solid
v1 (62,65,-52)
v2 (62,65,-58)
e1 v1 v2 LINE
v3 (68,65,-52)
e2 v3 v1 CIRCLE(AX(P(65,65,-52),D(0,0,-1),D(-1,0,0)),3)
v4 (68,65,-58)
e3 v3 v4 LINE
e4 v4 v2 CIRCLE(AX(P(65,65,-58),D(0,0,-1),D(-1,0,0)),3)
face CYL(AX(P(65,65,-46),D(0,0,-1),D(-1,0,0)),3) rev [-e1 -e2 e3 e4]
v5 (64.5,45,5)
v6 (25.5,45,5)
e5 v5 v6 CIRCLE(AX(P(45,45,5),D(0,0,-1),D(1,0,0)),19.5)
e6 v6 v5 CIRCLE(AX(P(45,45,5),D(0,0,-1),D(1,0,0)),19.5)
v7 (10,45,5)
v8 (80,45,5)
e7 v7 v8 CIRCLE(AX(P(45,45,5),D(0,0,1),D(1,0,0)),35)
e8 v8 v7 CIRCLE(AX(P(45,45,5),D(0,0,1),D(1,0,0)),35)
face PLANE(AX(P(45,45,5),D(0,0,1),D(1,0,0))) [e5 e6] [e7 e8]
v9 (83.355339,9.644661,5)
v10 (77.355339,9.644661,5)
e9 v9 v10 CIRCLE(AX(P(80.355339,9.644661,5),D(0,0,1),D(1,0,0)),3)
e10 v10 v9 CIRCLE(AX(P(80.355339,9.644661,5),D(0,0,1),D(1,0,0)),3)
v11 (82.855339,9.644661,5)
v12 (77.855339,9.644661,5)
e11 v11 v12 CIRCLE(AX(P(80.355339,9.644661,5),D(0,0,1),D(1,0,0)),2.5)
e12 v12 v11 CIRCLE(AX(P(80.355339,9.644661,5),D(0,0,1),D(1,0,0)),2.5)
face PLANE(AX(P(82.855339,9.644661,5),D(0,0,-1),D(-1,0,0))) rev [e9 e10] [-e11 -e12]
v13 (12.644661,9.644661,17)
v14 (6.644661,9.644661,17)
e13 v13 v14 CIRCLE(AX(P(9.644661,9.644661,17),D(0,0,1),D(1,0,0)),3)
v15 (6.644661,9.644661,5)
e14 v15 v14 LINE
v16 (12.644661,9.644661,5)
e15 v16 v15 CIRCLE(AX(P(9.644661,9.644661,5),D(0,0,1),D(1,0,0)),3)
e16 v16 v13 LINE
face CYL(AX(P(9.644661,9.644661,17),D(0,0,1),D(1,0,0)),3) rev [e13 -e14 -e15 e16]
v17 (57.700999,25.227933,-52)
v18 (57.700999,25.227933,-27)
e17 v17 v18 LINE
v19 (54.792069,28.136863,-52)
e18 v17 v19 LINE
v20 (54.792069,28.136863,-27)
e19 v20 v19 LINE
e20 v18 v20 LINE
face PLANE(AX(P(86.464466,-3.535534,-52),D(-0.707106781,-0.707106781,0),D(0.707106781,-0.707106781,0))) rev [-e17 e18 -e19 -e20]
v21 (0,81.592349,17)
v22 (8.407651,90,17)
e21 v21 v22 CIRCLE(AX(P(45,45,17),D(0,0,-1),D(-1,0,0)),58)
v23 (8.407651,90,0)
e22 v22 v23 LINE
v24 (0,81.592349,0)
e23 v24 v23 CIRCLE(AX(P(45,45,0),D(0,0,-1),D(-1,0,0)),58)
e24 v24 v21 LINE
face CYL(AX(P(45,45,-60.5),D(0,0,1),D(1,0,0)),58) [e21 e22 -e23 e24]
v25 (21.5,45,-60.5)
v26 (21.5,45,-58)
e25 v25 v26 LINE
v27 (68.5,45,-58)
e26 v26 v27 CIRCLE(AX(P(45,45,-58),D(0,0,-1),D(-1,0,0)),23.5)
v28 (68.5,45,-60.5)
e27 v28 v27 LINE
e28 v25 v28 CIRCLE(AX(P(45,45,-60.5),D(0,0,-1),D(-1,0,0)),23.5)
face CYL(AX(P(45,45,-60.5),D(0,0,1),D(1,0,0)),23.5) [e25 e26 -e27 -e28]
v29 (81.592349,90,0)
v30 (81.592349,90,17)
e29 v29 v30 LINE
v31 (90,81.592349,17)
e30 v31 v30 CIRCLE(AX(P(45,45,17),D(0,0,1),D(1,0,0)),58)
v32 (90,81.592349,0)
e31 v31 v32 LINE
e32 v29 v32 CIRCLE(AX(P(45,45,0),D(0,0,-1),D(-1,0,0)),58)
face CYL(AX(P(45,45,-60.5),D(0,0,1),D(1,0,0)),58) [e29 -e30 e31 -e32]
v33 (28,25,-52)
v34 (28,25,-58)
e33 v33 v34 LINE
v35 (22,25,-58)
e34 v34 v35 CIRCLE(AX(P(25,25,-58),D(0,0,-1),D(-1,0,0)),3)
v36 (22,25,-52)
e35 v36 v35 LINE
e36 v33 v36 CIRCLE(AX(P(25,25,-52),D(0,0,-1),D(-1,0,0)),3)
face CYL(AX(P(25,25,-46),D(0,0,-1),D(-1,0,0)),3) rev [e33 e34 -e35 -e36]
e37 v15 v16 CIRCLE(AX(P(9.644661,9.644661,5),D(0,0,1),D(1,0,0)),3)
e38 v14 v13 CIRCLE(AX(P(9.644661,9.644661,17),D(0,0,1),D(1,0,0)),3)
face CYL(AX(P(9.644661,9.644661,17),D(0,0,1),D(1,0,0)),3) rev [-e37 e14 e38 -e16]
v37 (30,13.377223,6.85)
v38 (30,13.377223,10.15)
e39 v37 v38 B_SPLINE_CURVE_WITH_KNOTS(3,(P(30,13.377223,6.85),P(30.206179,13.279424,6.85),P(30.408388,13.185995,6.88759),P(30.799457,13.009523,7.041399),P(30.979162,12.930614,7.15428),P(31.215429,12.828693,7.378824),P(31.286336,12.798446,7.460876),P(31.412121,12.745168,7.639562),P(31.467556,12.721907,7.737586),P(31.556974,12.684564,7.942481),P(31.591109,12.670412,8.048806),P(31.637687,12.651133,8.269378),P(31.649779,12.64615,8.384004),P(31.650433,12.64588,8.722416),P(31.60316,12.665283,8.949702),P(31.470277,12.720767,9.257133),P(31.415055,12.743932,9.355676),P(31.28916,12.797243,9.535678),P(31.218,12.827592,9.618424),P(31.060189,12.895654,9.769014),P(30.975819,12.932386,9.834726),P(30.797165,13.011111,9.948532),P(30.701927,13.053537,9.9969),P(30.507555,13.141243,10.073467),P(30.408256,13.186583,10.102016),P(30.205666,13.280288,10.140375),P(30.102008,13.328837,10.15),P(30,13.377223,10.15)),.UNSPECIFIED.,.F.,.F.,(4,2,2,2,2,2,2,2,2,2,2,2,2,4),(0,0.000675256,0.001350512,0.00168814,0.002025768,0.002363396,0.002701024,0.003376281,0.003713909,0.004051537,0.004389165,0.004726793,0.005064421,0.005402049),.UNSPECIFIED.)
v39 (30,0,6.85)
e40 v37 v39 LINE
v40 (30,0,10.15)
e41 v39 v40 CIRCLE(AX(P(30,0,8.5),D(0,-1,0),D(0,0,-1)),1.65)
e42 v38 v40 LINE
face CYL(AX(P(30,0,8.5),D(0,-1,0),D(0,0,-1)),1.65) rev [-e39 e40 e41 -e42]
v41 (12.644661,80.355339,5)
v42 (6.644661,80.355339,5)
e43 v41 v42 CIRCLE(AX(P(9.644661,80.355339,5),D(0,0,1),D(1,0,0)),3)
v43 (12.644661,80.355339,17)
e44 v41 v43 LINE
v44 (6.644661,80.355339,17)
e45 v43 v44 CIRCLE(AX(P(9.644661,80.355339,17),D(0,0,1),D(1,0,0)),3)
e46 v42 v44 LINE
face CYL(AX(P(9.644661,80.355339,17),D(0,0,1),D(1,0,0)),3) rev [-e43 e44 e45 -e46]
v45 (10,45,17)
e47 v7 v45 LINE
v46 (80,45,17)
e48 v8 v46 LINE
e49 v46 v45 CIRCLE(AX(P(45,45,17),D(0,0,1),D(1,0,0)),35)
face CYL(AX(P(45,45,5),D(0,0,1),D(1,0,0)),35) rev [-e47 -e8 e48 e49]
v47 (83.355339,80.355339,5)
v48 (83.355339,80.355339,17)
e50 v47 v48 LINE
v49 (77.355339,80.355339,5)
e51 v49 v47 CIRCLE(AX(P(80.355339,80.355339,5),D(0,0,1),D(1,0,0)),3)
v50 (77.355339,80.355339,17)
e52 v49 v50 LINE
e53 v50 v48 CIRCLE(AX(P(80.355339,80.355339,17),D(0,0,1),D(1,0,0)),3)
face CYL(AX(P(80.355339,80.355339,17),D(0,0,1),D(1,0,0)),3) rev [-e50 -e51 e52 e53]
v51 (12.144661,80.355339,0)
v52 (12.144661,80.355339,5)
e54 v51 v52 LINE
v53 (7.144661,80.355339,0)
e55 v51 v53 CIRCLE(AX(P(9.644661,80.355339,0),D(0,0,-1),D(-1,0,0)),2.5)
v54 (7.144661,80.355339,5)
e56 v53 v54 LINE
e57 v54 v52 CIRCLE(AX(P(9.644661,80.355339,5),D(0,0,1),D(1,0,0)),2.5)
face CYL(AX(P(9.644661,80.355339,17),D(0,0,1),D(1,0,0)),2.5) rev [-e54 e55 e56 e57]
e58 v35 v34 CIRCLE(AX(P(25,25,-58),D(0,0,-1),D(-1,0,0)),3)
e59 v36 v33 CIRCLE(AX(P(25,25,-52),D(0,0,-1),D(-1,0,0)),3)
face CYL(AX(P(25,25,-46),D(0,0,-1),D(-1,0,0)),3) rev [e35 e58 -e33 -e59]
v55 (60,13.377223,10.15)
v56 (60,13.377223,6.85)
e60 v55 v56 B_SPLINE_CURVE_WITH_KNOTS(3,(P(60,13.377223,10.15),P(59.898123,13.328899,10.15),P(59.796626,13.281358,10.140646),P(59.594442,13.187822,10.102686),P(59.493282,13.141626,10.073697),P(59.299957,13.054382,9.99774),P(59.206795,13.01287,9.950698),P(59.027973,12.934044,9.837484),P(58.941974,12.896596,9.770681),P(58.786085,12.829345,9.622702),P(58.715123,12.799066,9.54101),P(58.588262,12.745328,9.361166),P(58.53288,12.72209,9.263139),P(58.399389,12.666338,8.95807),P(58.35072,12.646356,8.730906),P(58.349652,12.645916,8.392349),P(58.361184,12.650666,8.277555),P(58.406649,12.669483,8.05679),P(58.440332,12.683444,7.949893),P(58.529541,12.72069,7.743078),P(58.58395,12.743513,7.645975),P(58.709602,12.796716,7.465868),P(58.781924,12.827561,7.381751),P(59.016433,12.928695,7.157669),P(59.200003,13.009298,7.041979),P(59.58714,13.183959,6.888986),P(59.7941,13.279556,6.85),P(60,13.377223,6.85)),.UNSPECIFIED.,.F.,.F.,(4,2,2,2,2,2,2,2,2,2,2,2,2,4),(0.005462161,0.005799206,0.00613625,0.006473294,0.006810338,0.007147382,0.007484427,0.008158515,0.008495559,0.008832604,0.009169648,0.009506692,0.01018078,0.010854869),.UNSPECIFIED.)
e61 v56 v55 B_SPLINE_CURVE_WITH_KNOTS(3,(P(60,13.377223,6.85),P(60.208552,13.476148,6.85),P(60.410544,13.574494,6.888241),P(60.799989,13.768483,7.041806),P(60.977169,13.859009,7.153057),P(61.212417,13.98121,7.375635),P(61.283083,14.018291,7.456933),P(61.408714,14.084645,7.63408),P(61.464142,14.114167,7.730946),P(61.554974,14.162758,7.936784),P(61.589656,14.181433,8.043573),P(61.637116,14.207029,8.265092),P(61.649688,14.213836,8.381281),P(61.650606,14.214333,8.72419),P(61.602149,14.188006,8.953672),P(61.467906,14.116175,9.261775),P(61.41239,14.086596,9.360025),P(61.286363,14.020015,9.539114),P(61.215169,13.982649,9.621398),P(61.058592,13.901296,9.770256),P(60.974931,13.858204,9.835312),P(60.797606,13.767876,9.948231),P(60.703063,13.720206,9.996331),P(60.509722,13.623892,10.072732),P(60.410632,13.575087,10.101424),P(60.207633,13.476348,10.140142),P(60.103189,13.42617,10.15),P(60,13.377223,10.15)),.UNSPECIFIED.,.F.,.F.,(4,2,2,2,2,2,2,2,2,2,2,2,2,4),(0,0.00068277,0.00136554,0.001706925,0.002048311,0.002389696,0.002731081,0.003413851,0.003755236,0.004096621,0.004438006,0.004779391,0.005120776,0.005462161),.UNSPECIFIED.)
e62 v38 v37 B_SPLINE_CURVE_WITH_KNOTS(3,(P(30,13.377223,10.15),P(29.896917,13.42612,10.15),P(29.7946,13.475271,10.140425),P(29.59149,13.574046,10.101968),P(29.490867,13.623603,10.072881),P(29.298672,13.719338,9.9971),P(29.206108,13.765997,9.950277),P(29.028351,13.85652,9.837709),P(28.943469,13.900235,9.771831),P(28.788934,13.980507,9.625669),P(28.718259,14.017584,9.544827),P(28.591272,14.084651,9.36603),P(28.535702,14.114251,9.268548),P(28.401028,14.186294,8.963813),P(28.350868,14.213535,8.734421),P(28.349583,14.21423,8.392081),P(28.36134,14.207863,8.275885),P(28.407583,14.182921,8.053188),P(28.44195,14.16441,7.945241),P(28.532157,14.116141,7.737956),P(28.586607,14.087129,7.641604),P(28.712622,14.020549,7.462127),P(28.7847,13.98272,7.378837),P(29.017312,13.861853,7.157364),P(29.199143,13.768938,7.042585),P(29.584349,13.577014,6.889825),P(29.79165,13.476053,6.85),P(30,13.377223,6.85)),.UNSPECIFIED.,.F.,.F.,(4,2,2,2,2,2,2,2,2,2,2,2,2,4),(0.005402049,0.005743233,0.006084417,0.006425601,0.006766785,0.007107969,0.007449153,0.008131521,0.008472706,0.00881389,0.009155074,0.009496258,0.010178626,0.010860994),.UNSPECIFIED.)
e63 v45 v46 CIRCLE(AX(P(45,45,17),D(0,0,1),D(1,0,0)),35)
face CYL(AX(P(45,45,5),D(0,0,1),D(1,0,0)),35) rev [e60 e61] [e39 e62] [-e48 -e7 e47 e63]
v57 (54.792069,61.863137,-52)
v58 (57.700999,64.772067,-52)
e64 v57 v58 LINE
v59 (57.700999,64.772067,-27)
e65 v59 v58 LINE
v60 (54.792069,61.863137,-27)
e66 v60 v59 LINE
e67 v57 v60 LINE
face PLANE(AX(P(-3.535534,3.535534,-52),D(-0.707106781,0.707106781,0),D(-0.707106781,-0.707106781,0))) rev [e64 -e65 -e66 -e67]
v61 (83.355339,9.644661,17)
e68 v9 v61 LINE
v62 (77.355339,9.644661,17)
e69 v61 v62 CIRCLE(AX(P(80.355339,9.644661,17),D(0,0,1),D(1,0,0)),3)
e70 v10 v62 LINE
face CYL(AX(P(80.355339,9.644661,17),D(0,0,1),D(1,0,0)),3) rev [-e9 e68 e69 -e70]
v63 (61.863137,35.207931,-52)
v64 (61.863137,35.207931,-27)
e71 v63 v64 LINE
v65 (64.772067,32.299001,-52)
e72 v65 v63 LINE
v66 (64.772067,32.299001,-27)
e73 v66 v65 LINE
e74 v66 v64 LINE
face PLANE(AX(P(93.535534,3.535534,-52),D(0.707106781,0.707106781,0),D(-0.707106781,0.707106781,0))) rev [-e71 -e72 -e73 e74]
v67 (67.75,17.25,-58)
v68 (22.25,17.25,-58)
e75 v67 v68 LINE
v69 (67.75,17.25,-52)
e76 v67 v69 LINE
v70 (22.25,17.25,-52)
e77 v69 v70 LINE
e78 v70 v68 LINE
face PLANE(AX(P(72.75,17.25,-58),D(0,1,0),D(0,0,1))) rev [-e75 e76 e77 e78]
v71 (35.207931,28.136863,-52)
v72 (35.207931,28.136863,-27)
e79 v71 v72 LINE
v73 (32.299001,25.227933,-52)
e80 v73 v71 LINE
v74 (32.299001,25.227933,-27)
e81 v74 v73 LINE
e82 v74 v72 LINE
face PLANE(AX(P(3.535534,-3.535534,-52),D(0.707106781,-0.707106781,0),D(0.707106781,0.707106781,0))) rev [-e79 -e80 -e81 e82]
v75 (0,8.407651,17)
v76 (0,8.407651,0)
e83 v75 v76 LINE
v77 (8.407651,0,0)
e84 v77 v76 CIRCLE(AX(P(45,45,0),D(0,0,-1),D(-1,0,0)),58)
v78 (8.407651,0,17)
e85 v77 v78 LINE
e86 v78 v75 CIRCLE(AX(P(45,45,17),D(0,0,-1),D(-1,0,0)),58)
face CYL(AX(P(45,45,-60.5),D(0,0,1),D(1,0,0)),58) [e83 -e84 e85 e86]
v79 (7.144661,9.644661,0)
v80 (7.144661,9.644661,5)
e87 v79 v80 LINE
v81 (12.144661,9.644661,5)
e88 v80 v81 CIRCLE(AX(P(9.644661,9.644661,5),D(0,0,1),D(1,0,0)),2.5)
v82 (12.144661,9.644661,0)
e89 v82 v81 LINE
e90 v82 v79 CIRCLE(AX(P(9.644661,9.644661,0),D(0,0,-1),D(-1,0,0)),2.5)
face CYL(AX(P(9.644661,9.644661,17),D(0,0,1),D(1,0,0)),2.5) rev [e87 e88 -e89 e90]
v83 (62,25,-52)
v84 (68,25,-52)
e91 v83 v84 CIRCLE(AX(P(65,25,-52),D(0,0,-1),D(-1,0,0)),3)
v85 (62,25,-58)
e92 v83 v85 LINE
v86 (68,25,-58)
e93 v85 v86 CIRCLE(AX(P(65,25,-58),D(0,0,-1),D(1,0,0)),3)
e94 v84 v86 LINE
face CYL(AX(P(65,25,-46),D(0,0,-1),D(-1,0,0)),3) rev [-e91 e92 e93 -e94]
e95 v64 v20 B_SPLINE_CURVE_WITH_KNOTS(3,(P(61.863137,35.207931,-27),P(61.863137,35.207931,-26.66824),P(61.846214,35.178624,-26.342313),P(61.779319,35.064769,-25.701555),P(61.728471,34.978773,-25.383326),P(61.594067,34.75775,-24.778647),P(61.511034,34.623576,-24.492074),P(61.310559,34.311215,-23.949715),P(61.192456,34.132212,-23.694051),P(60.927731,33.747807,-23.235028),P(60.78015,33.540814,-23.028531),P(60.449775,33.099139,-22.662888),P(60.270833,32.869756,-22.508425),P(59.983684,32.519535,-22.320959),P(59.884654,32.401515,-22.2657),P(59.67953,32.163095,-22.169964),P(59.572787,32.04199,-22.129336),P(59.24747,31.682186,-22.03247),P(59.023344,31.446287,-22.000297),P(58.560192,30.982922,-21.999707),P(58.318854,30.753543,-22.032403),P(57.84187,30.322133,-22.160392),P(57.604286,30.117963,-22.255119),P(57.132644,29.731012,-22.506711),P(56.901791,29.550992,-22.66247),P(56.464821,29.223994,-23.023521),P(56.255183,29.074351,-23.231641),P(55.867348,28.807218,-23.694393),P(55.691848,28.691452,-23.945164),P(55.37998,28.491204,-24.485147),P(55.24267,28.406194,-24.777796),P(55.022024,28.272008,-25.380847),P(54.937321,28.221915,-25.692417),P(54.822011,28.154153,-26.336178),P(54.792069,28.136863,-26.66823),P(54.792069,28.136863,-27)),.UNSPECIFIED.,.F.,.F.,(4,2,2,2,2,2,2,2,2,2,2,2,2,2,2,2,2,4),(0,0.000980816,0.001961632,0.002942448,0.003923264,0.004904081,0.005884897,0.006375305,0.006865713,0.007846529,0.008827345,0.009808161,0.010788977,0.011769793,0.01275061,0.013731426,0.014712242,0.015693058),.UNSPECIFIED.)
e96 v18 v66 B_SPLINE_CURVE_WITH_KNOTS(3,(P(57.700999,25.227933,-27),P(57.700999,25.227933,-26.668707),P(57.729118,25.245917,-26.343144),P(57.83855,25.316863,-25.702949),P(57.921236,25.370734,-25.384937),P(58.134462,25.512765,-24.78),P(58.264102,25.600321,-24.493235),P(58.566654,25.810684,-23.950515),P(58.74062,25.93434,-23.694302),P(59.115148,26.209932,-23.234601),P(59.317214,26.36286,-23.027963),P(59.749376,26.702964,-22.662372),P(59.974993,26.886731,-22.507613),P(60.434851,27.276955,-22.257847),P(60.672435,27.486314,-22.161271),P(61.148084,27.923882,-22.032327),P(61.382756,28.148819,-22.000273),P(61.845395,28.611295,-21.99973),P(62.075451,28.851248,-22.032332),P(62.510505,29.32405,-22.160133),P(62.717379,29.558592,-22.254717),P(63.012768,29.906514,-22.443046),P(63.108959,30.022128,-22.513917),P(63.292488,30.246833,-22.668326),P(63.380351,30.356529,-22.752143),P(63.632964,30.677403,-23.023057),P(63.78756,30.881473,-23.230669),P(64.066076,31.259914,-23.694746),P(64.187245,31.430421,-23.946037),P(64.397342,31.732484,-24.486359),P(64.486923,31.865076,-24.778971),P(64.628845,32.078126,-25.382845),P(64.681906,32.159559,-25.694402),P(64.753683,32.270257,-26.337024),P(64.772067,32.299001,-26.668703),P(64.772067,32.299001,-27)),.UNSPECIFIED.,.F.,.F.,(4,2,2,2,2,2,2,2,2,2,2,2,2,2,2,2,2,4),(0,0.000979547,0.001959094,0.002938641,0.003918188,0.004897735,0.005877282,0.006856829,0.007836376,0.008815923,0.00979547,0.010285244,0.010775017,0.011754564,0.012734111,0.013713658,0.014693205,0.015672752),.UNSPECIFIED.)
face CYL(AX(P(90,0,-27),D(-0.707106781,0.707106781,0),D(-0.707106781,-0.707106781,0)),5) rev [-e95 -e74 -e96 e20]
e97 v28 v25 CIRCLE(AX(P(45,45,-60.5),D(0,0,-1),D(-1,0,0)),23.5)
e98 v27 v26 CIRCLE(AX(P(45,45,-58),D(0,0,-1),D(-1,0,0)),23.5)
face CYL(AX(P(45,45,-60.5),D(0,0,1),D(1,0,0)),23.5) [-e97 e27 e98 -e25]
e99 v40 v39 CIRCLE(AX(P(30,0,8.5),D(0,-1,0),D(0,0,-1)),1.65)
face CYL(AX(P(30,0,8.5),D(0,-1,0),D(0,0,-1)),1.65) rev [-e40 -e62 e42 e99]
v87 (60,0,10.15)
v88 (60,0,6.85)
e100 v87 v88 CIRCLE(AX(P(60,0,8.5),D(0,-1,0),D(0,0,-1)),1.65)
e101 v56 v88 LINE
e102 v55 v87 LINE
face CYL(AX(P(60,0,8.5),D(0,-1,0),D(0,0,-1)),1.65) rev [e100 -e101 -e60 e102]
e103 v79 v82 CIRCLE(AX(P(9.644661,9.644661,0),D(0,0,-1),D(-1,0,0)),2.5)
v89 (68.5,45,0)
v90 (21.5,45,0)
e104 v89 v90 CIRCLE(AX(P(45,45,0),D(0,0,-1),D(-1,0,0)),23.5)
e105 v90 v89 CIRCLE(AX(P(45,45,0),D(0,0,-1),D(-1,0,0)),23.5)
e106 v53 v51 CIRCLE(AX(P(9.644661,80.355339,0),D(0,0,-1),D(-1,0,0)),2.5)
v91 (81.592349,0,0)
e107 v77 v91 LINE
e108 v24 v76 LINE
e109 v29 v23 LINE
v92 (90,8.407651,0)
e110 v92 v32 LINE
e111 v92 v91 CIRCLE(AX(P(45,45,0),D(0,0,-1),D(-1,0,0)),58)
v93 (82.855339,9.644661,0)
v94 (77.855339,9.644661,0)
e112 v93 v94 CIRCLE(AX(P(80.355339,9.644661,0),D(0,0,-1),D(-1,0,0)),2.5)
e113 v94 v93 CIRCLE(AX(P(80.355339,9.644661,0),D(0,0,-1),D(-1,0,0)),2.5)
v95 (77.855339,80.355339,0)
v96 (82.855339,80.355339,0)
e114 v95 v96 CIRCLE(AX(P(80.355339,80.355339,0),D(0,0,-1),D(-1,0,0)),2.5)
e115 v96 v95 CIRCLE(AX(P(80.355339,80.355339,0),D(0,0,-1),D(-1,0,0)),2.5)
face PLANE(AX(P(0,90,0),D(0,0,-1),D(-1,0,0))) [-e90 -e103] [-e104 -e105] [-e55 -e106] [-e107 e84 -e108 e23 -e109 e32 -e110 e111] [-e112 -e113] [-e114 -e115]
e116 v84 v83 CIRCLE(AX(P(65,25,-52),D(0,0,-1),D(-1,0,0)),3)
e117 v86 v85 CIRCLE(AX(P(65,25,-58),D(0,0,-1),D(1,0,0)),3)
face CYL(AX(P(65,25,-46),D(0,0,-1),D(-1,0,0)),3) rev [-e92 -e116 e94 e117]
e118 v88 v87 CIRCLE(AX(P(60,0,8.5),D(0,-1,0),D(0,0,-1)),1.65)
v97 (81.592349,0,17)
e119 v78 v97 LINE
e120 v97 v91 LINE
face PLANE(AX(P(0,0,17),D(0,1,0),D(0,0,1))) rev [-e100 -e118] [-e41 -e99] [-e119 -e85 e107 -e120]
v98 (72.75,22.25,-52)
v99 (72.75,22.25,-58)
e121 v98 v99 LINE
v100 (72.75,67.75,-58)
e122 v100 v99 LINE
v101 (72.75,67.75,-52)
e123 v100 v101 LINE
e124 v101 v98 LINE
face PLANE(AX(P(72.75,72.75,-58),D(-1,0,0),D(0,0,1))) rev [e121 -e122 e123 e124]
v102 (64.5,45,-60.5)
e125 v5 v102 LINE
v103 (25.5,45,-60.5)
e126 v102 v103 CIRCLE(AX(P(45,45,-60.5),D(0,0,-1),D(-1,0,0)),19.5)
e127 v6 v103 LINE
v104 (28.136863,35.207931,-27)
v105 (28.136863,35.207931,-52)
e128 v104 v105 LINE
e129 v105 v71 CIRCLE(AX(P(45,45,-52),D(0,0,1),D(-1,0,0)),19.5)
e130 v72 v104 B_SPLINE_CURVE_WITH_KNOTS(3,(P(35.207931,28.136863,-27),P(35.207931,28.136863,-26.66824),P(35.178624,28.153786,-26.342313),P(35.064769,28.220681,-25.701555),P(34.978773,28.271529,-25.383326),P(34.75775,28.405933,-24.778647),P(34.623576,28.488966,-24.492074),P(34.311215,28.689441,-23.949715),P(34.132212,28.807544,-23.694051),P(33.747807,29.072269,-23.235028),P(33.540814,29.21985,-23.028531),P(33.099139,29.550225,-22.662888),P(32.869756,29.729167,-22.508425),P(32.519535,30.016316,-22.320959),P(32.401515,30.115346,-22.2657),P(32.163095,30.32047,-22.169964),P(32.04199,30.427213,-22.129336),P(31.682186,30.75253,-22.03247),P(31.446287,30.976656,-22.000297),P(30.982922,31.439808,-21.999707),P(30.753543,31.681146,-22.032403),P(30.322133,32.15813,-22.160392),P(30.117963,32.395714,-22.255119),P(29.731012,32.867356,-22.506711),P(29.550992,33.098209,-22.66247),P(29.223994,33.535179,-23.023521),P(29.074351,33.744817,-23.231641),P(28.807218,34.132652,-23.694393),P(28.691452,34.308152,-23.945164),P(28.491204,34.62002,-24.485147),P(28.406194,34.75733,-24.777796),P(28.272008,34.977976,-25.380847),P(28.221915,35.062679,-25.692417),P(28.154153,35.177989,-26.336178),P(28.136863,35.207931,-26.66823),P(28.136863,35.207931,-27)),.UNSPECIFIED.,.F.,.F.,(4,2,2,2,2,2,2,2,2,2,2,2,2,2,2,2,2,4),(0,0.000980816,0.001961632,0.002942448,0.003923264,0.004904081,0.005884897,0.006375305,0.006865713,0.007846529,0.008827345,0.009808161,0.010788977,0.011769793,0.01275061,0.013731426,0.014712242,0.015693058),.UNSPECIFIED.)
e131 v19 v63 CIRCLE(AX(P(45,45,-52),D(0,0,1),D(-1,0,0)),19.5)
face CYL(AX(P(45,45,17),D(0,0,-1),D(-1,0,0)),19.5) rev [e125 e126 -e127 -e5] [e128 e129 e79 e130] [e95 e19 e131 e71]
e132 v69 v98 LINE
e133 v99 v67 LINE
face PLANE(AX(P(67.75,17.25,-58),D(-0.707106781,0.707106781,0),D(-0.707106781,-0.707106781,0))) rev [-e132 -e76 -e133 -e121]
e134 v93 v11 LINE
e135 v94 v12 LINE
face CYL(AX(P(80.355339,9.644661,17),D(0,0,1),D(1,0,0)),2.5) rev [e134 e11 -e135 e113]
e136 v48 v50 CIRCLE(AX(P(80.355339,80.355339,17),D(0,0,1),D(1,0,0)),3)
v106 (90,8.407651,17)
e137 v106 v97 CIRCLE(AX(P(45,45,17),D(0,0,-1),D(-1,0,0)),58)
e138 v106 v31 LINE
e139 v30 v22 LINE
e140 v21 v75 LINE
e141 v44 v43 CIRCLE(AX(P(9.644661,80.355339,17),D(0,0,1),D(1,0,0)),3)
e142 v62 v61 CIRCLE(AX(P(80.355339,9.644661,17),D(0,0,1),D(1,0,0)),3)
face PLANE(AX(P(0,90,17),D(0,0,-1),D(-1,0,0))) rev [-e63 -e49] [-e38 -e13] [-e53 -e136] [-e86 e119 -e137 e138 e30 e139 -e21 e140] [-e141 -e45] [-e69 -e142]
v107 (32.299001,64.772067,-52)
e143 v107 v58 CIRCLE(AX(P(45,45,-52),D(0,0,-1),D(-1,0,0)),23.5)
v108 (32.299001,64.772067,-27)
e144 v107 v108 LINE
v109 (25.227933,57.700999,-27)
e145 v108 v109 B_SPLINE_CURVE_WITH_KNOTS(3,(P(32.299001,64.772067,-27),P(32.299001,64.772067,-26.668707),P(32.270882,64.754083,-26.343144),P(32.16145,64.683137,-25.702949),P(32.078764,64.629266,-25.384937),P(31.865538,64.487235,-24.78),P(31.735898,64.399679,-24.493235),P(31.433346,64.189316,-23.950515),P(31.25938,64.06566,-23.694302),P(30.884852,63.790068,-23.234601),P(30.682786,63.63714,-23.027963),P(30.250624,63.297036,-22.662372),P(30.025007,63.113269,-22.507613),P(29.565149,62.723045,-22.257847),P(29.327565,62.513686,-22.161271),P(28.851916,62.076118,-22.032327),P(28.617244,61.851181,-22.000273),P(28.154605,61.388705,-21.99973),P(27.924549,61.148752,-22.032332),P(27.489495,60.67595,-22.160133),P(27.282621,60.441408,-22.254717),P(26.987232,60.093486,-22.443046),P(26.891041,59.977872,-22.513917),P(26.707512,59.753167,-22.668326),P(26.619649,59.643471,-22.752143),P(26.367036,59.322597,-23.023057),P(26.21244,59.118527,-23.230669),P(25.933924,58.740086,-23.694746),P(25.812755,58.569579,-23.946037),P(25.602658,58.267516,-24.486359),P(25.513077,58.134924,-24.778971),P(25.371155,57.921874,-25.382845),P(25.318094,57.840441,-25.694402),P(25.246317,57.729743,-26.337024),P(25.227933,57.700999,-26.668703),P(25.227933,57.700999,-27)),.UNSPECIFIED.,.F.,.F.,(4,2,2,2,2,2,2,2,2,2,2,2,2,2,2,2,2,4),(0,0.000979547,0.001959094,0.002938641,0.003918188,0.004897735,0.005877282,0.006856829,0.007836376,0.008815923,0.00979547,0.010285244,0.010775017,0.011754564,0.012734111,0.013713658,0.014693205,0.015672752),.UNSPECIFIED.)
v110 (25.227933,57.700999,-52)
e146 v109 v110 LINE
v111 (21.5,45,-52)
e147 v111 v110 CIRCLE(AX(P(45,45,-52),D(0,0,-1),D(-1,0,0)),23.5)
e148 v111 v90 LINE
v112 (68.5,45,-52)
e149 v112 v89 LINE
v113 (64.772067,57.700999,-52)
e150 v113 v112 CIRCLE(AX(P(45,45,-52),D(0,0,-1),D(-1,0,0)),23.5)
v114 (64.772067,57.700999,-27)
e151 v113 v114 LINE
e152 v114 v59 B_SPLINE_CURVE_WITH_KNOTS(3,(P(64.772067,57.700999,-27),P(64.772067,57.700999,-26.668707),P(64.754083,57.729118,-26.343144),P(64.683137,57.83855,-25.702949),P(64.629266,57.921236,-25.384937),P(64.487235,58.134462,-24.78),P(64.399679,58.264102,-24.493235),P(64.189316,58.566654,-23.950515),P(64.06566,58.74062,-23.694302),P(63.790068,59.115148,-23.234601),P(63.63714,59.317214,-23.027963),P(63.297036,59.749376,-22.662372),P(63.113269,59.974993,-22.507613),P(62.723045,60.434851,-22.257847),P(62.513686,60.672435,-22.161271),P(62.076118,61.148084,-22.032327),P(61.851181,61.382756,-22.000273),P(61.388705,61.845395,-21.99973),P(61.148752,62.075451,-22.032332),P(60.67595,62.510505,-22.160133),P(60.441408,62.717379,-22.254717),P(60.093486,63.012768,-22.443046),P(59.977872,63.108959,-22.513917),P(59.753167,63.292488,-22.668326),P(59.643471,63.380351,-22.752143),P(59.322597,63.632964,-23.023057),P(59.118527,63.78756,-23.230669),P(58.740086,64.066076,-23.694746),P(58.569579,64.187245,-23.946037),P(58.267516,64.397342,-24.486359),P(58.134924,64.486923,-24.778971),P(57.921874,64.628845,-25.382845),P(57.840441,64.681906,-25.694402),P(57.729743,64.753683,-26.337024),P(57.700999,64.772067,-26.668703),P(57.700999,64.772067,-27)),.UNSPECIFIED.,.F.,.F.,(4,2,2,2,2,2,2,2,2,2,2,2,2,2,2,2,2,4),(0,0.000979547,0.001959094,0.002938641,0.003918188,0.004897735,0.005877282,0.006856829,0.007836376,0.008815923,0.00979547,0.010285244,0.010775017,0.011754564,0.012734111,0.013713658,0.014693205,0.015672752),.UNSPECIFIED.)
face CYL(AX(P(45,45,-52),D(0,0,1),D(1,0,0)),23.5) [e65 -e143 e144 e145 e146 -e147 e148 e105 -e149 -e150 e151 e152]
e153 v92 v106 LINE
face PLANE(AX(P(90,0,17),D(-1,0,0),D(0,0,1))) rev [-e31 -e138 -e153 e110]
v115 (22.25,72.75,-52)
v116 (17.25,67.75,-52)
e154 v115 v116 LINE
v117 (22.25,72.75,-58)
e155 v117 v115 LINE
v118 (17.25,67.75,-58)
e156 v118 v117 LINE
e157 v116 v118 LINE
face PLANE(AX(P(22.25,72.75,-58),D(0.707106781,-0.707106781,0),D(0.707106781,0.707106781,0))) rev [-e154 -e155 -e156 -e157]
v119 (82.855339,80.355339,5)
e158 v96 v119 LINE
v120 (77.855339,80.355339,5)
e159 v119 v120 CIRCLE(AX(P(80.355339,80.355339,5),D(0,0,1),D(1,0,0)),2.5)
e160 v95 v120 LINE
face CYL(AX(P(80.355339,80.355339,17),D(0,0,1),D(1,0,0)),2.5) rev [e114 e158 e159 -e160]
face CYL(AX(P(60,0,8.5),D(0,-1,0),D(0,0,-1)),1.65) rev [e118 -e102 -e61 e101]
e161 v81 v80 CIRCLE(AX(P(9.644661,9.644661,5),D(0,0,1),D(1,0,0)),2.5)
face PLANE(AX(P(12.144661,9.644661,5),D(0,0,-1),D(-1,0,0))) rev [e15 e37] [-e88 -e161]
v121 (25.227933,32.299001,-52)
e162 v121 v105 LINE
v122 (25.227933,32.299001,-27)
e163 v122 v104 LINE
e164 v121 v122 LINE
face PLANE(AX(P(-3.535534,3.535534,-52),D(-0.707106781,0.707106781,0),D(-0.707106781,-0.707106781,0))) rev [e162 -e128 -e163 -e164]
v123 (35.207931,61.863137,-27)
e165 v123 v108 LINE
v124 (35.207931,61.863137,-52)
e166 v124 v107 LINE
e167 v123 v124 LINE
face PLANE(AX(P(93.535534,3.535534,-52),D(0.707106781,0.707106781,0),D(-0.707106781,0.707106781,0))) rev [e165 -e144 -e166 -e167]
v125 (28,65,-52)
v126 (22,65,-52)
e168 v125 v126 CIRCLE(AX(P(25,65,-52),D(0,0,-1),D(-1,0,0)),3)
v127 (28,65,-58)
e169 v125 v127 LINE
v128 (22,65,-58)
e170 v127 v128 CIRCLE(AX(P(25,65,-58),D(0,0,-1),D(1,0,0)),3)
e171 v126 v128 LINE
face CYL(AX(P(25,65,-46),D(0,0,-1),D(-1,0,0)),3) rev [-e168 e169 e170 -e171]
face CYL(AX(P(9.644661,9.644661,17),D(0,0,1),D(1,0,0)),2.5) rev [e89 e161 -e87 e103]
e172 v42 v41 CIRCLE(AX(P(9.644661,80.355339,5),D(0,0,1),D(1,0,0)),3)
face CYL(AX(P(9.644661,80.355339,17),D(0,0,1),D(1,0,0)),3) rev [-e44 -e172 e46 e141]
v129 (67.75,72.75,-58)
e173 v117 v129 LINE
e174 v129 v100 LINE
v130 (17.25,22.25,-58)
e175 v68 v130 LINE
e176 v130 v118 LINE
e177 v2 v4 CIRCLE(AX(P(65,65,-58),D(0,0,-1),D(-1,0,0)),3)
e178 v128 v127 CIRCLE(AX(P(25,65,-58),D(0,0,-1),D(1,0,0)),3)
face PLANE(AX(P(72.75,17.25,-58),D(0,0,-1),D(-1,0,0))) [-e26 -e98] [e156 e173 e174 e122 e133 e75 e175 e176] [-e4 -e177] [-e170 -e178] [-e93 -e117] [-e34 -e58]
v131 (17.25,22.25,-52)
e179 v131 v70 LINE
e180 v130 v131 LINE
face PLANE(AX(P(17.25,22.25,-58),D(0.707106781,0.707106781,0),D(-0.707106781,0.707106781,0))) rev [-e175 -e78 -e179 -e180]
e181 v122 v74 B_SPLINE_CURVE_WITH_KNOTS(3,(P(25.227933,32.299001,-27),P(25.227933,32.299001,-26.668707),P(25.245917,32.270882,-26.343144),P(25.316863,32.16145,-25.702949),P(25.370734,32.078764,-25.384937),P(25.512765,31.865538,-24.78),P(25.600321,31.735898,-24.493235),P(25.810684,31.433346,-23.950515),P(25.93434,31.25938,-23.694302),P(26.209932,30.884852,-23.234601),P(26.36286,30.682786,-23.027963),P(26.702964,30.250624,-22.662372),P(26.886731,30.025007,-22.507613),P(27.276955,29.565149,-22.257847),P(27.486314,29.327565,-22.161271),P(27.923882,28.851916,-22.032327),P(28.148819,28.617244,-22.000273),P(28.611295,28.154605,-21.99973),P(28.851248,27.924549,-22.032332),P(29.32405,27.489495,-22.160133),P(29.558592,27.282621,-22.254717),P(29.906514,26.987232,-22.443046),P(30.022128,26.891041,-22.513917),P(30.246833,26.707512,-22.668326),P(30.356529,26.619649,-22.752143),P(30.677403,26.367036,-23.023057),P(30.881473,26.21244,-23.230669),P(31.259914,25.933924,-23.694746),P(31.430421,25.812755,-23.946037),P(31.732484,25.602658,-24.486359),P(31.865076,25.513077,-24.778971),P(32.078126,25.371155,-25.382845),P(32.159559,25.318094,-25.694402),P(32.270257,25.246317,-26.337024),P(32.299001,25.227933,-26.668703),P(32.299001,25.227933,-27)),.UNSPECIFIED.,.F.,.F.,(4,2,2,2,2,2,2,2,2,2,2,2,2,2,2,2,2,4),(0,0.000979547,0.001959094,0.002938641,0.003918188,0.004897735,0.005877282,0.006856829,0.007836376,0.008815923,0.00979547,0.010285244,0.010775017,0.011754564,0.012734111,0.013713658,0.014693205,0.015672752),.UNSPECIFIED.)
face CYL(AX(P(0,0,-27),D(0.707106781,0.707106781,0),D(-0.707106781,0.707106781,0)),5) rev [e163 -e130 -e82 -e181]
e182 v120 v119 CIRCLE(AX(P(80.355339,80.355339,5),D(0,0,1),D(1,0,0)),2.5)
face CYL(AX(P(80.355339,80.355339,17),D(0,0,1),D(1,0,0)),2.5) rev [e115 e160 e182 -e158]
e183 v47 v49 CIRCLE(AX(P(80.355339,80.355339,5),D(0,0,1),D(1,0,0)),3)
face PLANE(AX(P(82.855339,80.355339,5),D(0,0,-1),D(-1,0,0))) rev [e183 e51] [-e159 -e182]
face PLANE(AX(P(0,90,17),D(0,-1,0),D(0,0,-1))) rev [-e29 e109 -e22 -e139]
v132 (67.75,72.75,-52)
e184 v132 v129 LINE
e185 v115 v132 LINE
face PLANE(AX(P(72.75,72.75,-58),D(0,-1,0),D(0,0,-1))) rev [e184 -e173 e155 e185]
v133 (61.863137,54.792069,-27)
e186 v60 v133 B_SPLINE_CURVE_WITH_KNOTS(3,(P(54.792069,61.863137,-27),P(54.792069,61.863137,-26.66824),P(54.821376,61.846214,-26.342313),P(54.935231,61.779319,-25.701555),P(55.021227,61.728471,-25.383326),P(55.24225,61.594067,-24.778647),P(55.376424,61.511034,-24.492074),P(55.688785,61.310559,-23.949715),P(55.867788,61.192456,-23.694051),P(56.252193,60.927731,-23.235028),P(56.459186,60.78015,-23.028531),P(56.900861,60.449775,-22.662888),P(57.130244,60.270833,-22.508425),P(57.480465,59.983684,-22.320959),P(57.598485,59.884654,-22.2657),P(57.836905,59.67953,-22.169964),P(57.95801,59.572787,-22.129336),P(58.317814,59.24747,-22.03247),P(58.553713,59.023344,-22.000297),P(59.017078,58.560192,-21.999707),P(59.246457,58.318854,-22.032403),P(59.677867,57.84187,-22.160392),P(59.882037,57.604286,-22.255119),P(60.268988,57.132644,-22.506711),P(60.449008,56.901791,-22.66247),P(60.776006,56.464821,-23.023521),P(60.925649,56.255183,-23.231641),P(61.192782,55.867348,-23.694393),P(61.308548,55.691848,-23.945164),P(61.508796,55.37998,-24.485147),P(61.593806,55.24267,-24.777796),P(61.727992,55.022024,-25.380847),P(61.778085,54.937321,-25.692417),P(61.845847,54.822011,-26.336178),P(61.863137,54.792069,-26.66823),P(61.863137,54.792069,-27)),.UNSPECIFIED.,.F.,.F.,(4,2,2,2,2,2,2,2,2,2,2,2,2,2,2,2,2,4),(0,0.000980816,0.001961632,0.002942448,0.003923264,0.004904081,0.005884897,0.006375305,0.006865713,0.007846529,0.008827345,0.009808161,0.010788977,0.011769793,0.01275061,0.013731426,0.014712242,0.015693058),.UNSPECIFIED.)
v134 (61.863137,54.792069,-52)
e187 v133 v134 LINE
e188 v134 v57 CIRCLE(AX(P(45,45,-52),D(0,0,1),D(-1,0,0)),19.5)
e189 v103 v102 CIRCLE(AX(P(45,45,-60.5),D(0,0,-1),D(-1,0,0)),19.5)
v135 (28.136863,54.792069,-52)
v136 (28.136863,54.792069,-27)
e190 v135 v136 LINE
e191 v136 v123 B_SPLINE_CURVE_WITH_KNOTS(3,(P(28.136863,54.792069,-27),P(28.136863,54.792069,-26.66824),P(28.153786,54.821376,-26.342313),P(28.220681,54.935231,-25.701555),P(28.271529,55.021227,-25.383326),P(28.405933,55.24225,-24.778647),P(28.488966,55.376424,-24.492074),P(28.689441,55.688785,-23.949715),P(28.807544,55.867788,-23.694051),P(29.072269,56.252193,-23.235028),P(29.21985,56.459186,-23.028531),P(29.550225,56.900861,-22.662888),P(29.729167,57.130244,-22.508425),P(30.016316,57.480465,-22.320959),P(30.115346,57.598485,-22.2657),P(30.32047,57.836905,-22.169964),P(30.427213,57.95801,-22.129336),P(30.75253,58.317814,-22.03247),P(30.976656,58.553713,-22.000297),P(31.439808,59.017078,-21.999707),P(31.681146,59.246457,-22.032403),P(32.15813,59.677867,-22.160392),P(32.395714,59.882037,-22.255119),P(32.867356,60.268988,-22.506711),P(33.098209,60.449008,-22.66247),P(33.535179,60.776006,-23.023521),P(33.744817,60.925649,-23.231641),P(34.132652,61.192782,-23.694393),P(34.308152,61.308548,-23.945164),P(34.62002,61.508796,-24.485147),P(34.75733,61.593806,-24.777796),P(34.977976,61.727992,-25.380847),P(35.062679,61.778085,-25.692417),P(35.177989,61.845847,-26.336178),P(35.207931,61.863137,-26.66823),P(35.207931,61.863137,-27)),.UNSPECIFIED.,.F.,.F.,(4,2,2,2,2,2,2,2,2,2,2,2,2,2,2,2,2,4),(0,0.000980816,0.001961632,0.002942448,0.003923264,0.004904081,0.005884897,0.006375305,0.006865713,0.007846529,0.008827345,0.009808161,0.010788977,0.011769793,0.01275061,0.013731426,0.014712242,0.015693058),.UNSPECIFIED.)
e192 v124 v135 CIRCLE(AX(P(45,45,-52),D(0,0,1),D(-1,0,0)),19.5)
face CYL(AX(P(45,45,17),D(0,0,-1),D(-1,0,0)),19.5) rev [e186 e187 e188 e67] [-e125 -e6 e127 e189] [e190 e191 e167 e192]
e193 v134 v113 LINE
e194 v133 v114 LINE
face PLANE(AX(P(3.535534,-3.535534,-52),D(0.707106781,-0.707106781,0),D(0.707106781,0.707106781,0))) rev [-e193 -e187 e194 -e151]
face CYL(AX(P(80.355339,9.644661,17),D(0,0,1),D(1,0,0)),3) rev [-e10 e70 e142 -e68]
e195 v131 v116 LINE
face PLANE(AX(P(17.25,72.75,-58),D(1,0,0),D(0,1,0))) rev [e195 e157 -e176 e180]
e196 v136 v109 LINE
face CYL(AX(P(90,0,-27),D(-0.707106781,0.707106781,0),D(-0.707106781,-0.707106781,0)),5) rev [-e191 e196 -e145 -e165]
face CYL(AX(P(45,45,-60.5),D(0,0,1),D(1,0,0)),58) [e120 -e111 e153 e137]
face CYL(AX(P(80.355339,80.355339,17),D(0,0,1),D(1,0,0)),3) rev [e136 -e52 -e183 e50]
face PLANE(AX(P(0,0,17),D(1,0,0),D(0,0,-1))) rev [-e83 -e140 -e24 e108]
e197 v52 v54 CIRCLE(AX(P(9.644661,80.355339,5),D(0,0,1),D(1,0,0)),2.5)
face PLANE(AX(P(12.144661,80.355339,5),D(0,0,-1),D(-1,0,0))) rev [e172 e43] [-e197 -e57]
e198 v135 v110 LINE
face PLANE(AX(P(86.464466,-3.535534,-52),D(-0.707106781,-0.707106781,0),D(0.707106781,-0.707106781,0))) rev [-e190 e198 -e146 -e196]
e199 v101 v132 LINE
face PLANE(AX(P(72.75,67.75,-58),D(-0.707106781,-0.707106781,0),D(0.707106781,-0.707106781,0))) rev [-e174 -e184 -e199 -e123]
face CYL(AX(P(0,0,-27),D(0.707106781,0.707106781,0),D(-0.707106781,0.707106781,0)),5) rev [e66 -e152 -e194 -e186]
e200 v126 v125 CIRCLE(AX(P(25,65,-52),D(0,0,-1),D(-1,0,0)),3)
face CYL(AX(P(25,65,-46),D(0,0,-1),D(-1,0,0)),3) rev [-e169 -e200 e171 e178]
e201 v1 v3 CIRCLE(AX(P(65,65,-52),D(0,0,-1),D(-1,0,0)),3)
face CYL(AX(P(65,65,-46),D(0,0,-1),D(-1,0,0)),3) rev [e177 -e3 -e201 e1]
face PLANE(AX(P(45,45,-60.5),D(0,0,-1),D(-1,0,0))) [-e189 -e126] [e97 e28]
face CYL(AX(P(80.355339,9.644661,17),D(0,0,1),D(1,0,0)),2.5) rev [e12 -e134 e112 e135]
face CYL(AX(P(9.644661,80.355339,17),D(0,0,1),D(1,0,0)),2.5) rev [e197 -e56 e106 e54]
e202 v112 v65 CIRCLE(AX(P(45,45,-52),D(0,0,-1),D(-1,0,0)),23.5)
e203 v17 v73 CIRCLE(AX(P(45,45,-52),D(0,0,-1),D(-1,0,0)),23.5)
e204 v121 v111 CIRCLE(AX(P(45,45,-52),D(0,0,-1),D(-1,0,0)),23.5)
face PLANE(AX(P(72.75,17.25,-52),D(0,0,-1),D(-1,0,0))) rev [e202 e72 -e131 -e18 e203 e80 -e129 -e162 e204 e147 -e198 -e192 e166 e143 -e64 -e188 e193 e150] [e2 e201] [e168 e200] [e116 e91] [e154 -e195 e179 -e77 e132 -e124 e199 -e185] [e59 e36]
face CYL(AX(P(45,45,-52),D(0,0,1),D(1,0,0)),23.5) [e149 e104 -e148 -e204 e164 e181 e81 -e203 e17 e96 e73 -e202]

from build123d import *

# Parameters (mm, degrees)
SKETCH_1_W                   = 90
SKETCH_1_H                   = 90
EXTRUDE_1_DEPTH              = 17
SKETCH_2_R                   = 23.5
EXTRUDE_2_DEPTH              = 52
SKETCH_3_W                   = 55.5
SKETCH_3_H                   = 55.5
EXTRUDE_3_DEPTH              = 6
SKETCH_4_R                   = 23.5
EXTRUDE_4_DEPTH              = 2.5
SKETCH_5_R                   = 19.5
CUT_EXTRUDE_1_DEPTH          = 150.017616408
HOLE_WIZARD_M6_1_D           = 5
HOLE_WIZARD_M6_1_CBORE_D     = 6
HOLE_WIZARD_M6_1_CBORE_DEPTH = 12
SKETCH_8_R                   = 35
CUT_EXTRUDE_2_DEPTH          = 12
SKETCH_9_OUTSIDE_W           = 121.804
SKETCH_9_OUTSIDE_H           = 121.804
SKETCH_9_OUTSIDE_R           = 58
CUT_EXTRUDE_3_DEPTH          = 150.017616408
SKETCH_10_R                  = 3
CUT_EXTRUDE_4_DEPTH          = 12
CHAMFER_1_SIZE               = 5
CUT_EXTRUDE_5_DEPTH          = 146.62895586
CUT_EXTRUDE_6_DEPTH          = 118.175389983
HOLE_WIZARD_M4_1_REACH       = 142.926
HOLE_WIZARD_M4_1_BORE_R      = 1.65


with BuildPart() as part:
    # 草图1 → 拉伸1 (new body)
    with BuildSketch(Plane.XY):
        with Locations((45, 45)):
            Rectangle(SKETCH_1_W, SKETCH_1_H)
    extrude(amount=EXTRUDE_1_DEPTH)

    # 草图2 → 拉伸2 (add)
    with BuildSketch(Plane(origin=(0, 0, 0), x_dir=(-1, 0, 0), z_dir=(0, 0, -1))):
        with Locations(Location((-45, 45, 0), (0, 0, 180))):
            Circle(SKETCH_2_R)
    extrude(amount=EXTRUDE_2_DEPTH)

    # 草图3 → 拉伸3 (add)
    with BuildSketch(Plane(origin=(0, 0, -52), x_dir=(-1, 0, 0), z_dir=(0, 0, -1))):
        with Locations((-45, 45)):
            Rectangle(SKETCH_3_W, SKETCH_3_H)
    extrude(amount=EXTRUDE_3_DEPTH)

    # 草图4 → 拉伸4 (add)
    with BuildSketch(Plane(origin=(0, 0, -58), x_dir=(-1, 0, 0), z_dir=(0, 0, -1))):
        with Locations(Location((-45, 45, 0), (0, 0, 180))):
            Circle(SKETCH_4_R)
    extrude(amount=EXTRUDE_4_DEPTH)

    # 草图5 → 切除-拉伸1 (cut, through all)
    with BuildSketch(Plane(origin=(0, 0, -60.5), x_dir=(-1, 0, 0), z_dir=(0, 0, -1))):
        with Locations((-45, 45)):
            Circle(SKETCH_5_R)
    extrude(amount=-CUT_EXTRUDE_1_DEPTH, mode=Mode.SUBTRACT)

    # M6 螺纹孔1 (through all)
    with Locations(Plane(origin=(9.644660941, 80.355339059, 17), x_dir=(1, 0, 0), z_dir=(0, 0, 1))):
        with Locations((0, 0), (70.710678118, 0), (0, -70.710678118), (70.710678118, -70.710678118)):
            CounterBoreHole(HOLE_WIZARD_M6_1_D / 2, HOLE_WIZARD_M6_1_CBORE_D / 2, HOLE_WIZARD_M6_1_CBORE_DEPTH)

    # 草图8 → 切除-拉伸2 (cut)
    with BuildSketch(Plane.XY.offset(17)):
        with Locations((45, 45)):
            Circle(SKETCH_8_R)
    extrude(amount=-CUT_EXTRUDE_2_DEPTH, mode=Mode.SUBTRACT)

    # 草图9 outside → 切除-拉伸3 (cut, through all)
    with BuildSketch(Plane.XY.offset(17)):
        with Locations((45, 45)):
            Rectangle(SKETCH_9_OUTSIDE_W, SKETCH_9_OUTSIDE_H)
        with Locations((45, 45)):
            Circle(SKETCH_9_OUTSIDE_R, mode=Mode.SUBTRACT)
    extrude(amount=-CUT_EXTRUDE_3_DEPTH, mode=Mode.SUBTRACT)

    # 草图10 → 切除-拉伸4 (cut)
    with BuildSketch(Plane(origin=(0, 0, -58), x_dir=(-1, 0, 0), z_dir=(0, 0, -1))):
        with Locations((-65, 65)):
            Circle(SKETCH_10_R)
        with Locations((-25, 65)):
            Circle(SKETCH_10_R)
        with Locations((-25, 25)):
            Circle(SKETCH_10_R)
        with Locations((-65, 25)):
            Circle(SKETCH_10_R)
    extrude(amount=-CUT_EXTRUDE_4_DEPTH, mode=Mode.SUBTRACT)

    # 倒角1
    chamfer_1_edges = [part.edges().sort_by_distance(p)[0] for p in [
        (72.75, 72.75, -55),
        (72.75, 17.25, -55),
        (17.25, 17.25, -55),
        (17.25, 72.75, -55),
    ]]
    chamfer(chamfer_1_edges, length=CHAMFER_1_SIZE)

    # 草图11 → 切除-拉伸5 (cut, through all)
    with BuildSketch(Plane(origin=(-25.957106781, 25.957106781, 0), x_dir=(0, 0, 1), z_dir=(-0.7071067811865485, 0.7071067811865467, 0))):
        with BuildLine():
            Line((-52, 58.639610307), (-27, 58.639610307))
            ThreePointArc((-27, 58.639610307), (-22, 63.639610307), (-27, 68.639610307))
            Line((-27, 68.639610307), (-52, 68.639610307))
            Line((-52, 68.639610307), (-52, 58.639610307))
        make_face()
    extrude(amount=-CUT_EXTRUDE_5_DEPTH, mode=Mode.SUBTRACT)

    # 草图12 → 切除-拉伸6 (cut, through all)
    with BuildSketch(Plane(origin=(70.957106781, 70.957106781, 0), x_dir=(-0.7071067811865485, 0.7071067811865467, 0), z_dir=(0.7071067811865467, 0.7071067811865485, 0))):
        with BuildLine():
            Line((-5, -52), (5, -52))
            Line((5, -52), (5, -27))
            ThreePointArc((5, -27), (0, -22), (-5, -27))
            Line((-5, -27), (-5, -52))
        make_face()
    extrude(amount=-CUT_EXTRUDE_6_DEPTH, mode=Mode.SUBTRACT)

    # M4 螺纹孔1 bore → M4 螺纹孔1 (cut, up to next)
    with BuildSketch(Plane.XZ, mode=Mode.PRIVATE) as hole_wizard_m4_1_sk1:
        with Locations((60, 8.5)):
            Circle(HOLE_WIZARD_M4_1_BORE_R)
    hole_wizard_m4_1_tool1 = extrude(hole_wizard_m4_1_sk1.sketch, amount=-HOLE_WIZARD_M4_1_REACH, mode=Mode.PRIVATE) & part.part
    # M4 螺纹孔1 bore → M4 螺纹孔1 (cut, up to next)
    with BuildSketch(Plane.XZ, mode=Mode.PRIVATE) as hole_wizard_m4_1_sk2:
        with Locations((30, 8.5)):
            Circle(HOLE_WIZARD_M4_1_BORE_R)
    hole_wizard_m4_1_tool2 = extrude(hole_wizard_m4_1_sk2.sketch, amount=-HOLE_WIZARD_M4_1_REACH, mode=Mode.PRIVATE) & part.part
    add(hole_wizard_m4_1_tool1.solids().sort_by_distance((60, 0, 8.5))[0], mode=Mode.SUBTRACT)
    add(hole_wizard_m4_1_tool2.solids().sort_by_distance((30, 0, 8.5))[0], mode=Mode.SUBTRACT)


solid = part.part
